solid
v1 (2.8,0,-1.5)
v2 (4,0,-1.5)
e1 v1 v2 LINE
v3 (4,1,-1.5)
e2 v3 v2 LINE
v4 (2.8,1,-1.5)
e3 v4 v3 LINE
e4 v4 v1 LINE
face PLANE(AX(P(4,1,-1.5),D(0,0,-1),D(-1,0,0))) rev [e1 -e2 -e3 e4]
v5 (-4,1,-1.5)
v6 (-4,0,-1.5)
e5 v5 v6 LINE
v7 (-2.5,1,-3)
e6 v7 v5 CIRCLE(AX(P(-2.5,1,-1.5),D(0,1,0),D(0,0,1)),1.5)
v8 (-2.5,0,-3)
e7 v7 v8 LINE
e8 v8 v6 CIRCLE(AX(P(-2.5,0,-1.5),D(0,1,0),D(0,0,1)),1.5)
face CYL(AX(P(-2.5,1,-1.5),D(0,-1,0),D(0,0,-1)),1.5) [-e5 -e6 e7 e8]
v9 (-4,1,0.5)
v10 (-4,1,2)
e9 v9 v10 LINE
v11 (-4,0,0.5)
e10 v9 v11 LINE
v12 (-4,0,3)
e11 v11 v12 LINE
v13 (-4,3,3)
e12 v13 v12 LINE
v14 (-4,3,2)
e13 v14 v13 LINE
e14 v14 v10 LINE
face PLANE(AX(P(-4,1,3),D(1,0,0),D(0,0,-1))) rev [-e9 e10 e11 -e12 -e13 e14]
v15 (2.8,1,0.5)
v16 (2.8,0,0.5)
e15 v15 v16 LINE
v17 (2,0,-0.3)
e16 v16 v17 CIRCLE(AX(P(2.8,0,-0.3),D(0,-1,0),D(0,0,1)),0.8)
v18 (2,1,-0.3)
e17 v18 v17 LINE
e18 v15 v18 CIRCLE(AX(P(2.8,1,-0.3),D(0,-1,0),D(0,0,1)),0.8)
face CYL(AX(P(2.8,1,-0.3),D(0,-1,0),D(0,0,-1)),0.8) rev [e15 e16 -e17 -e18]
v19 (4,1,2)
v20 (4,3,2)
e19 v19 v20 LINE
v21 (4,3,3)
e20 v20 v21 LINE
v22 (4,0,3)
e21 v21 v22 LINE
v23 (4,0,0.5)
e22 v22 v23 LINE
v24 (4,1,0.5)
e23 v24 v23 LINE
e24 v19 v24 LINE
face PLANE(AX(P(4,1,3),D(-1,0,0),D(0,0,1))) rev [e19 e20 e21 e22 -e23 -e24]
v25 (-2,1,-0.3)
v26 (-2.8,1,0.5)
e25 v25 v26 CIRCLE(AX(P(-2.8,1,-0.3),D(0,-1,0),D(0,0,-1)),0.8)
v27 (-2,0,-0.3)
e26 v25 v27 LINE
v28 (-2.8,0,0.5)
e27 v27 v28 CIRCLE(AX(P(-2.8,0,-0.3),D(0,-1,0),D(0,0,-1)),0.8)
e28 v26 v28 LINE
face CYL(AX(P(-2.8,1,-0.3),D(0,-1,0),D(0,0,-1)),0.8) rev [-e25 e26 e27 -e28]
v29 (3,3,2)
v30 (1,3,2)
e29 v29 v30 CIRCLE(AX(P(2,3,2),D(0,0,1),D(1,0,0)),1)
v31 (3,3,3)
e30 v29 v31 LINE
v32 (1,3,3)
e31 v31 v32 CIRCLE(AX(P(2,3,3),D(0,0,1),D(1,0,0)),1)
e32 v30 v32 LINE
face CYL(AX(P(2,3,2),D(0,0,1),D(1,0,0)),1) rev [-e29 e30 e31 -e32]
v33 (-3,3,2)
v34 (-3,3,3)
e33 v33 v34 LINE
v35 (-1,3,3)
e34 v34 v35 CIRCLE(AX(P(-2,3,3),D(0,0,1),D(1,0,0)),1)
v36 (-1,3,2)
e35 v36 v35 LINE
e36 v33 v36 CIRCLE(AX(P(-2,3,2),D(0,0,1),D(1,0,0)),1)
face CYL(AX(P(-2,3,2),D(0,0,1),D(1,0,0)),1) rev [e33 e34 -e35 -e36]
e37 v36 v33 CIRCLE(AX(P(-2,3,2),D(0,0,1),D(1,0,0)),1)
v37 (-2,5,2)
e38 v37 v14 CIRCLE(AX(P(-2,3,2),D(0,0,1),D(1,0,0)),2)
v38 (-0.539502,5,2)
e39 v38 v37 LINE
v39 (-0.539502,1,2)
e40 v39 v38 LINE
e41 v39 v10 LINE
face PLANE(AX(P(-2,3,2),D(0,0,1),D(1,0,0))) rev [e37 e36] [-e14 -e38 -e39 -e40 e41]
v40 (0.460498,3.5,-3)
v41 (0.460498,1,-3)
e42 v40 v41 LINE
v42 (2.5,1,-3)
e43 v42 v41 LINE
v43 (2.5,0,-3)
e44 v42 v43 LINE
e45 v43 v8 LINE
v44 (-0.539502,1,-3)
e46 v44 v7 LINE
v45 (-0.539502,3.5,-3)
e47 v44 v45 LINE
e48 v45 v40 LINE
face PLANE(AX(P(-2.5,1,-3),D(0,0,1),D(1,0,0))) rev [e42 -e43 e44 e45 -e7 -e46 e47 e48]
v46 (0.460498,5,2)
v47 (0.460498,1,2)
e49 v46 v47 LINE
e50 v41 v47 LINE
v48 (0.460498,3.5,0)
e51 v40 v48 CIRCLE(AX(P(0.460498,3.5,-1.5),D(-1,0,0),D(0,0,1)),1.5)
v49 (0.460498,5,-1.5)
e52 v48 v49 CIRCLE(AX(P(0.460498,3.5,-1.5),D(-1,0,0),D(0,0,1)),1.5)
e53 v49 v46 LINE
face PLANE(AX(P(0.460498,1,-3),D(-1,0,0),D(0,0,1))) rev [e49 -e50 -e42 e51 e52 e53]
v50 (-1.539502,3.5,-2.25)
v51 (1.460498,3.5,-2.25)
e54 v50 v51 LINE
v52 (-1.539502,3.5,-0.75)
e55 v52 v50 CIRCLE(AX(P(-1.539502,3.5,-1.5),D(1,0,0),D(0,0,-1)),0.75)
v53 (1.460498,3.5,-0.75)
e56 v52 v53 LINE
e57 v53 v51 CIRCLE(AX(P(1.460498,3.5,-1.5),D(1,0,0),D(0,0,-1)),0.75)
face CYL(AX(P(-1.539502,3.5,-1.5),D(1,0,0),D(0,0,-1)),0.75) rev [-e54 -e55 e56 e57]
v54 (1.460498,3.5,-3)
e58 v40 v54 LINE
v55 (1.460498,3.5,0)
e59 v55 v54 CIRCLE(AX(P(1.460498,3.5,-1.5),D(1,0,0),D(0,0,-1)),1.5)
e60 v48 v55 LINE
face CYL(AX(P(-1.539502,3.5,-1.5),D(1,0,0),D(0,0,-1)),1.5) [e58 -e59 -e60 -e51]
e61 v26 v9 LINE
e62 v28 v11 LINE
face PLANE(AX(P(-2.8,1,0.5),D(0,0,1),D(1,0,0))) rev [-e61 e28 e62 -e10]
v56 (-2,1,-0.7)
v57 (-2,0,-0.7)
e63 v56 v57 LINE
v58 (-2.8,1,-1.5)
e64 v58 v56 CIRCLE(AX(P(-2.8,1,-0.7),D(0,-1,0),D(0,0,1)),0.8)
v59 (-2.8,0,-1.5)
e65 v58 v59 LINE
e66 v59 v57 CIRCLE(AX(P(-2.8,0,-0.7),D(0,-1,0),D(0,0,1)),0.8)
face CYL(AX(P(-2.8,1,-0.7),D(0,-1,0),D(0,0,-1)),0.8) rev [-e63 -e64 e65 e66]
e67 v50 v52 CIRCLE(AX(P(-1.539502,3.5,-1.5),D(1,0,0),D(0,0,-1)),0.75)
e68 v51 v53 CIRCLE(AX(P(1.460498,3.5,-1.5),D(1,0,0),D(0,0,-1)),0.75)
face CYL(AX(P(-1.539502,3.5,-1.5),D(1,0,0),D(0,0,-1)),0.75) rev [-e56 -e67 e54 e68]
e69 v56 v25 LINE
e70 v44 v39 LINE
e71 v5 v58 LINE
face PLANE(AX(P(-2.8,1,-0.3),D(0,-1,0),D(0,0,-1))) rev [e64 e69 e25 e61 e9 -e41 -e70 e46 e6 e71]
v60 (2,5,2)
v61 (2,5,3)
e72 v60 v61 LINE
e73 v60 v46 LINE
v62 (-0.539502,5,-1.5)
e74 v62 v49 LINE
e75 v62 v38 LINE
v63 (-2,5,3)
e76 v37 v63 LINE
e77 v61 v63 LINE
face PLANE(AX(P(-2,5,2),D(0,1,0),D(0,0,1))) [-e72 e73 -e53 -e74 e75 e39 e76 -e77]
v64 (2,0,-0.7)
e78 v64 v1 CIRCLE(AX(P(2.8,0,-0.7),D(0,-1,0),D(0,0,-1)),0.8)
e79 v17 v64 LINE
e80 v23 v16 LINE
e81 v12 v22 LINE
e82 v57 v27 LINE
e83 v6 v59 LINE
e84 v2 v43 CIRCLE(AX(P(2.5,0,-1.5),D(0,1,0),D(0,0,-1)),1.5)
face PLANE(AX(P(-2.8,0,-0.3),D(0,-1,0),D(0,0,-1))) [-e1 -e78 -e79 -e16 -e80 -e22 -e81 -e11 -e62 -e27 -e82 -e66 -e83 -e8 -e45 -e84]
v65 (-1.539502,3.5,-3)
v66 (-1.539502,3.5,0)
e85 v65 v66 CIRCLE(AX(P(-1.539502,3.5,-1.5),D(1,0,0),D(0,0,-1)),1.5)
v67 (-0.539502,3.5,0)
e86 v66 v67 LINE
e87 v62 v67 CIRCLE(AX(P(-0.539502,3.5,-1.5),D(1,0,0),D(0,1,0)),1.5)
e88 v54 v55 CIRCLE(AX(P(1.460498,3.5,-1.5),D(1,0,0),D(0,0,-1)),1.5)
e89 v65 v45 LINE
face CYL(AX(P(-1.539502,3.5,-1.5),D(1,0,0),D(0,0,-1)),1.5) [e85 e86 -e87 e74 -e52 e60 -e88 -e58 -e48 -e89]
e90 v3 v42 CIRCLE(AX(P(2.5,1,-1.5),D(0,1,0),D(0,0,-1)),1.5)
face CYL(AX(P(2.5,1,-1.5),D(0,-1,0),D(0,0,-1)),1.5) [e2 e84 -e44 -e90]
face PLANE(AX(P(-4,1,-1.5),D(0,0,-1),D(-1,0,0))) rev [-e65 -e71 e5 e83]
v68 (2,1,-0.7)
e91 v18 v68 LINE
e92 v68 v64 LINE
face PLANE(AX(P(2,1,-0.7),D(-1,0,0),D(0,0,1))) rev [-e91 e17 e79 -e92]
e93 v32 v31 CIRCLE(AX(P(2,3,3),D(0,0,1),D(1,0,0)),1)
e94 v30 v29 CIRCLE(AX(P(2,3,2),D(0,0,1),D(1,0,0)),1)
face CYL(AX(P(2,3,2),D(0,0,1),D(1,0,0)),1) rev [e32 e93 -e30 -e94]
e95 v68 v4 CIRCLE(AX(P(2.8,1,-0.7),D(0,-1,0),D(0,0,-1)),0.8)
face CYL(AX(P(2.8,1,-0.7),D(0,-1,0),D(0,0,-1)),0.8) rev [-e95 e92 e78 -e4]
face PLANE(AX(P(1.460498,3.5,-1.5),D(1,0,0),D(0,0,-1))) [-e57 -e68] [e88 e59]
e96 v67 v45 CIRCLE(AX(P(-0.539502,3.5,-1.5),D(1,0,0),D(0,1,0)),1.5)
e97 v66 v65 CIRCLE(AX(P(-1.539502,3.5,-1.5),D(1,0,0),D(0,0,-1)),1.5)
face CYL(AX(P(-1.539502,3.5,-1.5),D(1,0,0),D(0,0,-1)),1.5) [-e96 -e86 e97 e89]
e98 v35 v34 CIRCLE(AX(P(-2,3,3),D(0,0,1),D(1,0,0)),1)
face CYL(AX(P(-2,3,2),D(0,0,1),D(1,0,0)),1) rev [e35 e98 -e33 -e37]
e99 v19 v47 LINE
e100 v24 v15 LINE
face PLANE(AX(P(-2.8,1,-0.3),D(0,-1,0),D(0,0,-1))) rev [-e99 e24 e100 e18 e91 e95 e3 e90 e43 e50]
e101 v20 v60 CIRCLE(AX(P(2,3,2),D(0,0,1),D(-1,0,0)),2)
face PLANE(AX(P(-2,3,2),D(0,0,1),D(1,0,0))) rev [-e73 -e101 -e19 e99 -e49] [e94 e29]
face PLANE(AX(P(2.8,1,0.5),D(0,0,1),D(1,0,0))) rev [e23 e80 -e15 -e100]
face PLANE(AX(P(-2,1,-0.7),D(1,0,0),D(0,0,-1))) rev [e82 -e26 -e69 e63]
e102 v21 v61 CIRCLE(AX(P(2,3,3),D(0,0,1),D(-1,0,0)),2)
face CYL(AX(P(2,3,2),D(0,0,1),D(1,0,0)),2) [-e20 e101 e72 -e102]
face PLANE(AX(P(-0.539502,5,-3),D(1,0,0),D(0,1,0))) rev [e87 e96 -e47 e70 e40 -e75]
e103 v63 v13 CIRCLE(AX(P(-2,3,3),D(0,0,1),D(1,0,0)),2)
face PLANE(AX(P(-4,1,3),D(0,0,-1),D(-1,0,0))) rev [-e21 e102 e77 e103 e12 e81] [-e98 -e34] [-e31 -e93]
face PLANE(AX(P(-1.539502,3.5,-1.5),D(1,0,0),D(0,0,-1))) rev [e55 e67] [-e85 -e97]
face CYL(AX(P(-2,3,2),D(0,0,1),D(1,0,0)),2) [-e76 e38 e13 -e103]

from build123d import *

# Parameters (mm, degrees)
BASE_PLATE_DEPTH       = 1
UPRIGHT_PLATE_SKETCH_R = 1
UPRIGHT_PLATE_DEPTH    = 1
RIB_SKETCH_W           = 1
RIB_SKETCH_H           = 4
RIB_DEPTH              = 5
PIVOT_HUB_DEPTH        = 1
PIVOT_HUB_DEPTH_BACK   = 2
PIVOT_HUB_SKETCH_R     = 1.5
HUB_BORE_SKETCH_R      = 0.75
HUB_BORE_DEPTH         = 3
SLOT_CUT_DEPTH         = 3


with BuildPart() as part:
    # Base Plate Sketch → Base Plate (new body)
    with BuildSketch(Plane(origin=(0, 0, 0), x_dir=(1, 0, 0), z_dir=(0, 1, 0))):
        with BuildLine():
            Line((-4, 1.5), (-2.8, 1.5))
            ThreePointArc((-2.8, 1.5), (-2.234314575, 1.265685425), (-2, 0.7))
            Line((-2, 0.7), (-2, 0.3))
            ThreePointArc((-2, 0.3), (-2.234314575, -0.265685425), (-2.8, -0.5))
            Line((-2.8, -0.5), (-4, -0.5))
            Line((-4, -0.5), (-4, -3))
            Line((-4, -3), (4, -3))
            Line((4, -3), (4, -0.5))
            Line((4, -0.5), (2.8, -0.5))
            ThreePointArc((2.8, -0.5), (2.234314575, -0.265685425), (2, 0.3))
            Line((2, 0.3), (2, 0.7))
            ThreePointArc((2, 0.7), (2.234314575, 1.265685425), (2.8, 1.5))
            Line((2.8, 1.5), (4, 1.5))
            ThreePointArc((4, 1.5), (3.560660172, 2.560660172), (2.5, 3))
            Line((2.5, 3), (-2.5, 3))
            ThreePointArc((-2.5, 3), (-3.560660172, 2.560660172), (-4, 1.5))
        make_face()
    extrude(amount=BASE_PLATE_DEPTH)

    # Upright Plate Sketch → Upright Plate (add)
    with BuildSketch(Plane.XY.offset(3)):
        with BuildLine():
            Line((-4, 0), (4, 0))
            Line((4, 0), (4, 3))
            ThreePointArc((4, 3), (3.414213562, 4.414213562), (2, 5))
            Line((2, 5), (-2, 5))
            ThreePointArc((-2, 5), (-3.414213562, 4.414213562), (-4, 3))
            Line((-4, 3), (-4, 0))
        make_face()
        with Locations((-2, 3)):
            Circle(UPRIGHT_PLATE_SKETCH_R, mode=Mode.SUBTRACT)
        with Locations((2, 3)):
            Circle(UPRIGHT_PLATE_SKETCH_R, mode=Mode.SUBTRACT)
    extrude(amount=-UPRIGHT_PLATE_DEPTH)

    # Rib Sketch → Rib (add)
    with BuildSketch(Plane(origin=(0, 0, 2), x_dir=(-1, 0, 0), z_dir=(0, 0, -1))):
        with Locations((0.039501807, 3)):
            Rectangle(RIB_SKETCH_W, RIB_SKETCH_H)
    extrude(amount=RIB_DEPTH)

    # Pivot Hub Sketch → Pivot Hub (add, two sides: drawn at the far end of the back side and taken through both)
    with BuildSketch(Plane(origin=(0.460498193, 0, 0), x_dir=(0, 0, -1), z_dir=(1, 0, 0)).offset(-PIVOT_HUB_DEPTH_BACK)):
        with Locations((1.5, 3.5)):
            Circle(PIVOT_HUB_SKETCH_R)
    extrude(amount=PIVOT_HUB_DEPTH + PIVOT_HUB_DEPTH_BACK)

    # Hub Bore Sketch → Hub Bore (cut)
    with BuildSketch(Plane(origin=(1.460498193, 0, 0), x_dir=(0, 0, -1), z_dir=(1, 0, 0))):
        with Locations((1.5, 3.5)):
            Circle(HUB_BORE_SKETCH_R)
    extrude(amount=-HUB_BORE_DEPTH, mode=Mode.SUBTRACT)

    # Slot Cut Sketch → Slot Cut (cut)
    with BuildSketch(Plane(origin=(0.460498193, 0, 0), x_dir=(0, 0, -1), z_dir=(1, 0, 0))):
        with BuildLine():
            Line((1.5, 5), (3, 5))
            Line((3, 5), (3, 3.5))
            ThreePointArc((3, 3.5), (2.560660172, 4.560660172), (1.5, 5))
        make_face()
    extrude(amount=-SLOT_CUT_DEPTH, mode=Mode.SUBTRACT)


solid = part.part
